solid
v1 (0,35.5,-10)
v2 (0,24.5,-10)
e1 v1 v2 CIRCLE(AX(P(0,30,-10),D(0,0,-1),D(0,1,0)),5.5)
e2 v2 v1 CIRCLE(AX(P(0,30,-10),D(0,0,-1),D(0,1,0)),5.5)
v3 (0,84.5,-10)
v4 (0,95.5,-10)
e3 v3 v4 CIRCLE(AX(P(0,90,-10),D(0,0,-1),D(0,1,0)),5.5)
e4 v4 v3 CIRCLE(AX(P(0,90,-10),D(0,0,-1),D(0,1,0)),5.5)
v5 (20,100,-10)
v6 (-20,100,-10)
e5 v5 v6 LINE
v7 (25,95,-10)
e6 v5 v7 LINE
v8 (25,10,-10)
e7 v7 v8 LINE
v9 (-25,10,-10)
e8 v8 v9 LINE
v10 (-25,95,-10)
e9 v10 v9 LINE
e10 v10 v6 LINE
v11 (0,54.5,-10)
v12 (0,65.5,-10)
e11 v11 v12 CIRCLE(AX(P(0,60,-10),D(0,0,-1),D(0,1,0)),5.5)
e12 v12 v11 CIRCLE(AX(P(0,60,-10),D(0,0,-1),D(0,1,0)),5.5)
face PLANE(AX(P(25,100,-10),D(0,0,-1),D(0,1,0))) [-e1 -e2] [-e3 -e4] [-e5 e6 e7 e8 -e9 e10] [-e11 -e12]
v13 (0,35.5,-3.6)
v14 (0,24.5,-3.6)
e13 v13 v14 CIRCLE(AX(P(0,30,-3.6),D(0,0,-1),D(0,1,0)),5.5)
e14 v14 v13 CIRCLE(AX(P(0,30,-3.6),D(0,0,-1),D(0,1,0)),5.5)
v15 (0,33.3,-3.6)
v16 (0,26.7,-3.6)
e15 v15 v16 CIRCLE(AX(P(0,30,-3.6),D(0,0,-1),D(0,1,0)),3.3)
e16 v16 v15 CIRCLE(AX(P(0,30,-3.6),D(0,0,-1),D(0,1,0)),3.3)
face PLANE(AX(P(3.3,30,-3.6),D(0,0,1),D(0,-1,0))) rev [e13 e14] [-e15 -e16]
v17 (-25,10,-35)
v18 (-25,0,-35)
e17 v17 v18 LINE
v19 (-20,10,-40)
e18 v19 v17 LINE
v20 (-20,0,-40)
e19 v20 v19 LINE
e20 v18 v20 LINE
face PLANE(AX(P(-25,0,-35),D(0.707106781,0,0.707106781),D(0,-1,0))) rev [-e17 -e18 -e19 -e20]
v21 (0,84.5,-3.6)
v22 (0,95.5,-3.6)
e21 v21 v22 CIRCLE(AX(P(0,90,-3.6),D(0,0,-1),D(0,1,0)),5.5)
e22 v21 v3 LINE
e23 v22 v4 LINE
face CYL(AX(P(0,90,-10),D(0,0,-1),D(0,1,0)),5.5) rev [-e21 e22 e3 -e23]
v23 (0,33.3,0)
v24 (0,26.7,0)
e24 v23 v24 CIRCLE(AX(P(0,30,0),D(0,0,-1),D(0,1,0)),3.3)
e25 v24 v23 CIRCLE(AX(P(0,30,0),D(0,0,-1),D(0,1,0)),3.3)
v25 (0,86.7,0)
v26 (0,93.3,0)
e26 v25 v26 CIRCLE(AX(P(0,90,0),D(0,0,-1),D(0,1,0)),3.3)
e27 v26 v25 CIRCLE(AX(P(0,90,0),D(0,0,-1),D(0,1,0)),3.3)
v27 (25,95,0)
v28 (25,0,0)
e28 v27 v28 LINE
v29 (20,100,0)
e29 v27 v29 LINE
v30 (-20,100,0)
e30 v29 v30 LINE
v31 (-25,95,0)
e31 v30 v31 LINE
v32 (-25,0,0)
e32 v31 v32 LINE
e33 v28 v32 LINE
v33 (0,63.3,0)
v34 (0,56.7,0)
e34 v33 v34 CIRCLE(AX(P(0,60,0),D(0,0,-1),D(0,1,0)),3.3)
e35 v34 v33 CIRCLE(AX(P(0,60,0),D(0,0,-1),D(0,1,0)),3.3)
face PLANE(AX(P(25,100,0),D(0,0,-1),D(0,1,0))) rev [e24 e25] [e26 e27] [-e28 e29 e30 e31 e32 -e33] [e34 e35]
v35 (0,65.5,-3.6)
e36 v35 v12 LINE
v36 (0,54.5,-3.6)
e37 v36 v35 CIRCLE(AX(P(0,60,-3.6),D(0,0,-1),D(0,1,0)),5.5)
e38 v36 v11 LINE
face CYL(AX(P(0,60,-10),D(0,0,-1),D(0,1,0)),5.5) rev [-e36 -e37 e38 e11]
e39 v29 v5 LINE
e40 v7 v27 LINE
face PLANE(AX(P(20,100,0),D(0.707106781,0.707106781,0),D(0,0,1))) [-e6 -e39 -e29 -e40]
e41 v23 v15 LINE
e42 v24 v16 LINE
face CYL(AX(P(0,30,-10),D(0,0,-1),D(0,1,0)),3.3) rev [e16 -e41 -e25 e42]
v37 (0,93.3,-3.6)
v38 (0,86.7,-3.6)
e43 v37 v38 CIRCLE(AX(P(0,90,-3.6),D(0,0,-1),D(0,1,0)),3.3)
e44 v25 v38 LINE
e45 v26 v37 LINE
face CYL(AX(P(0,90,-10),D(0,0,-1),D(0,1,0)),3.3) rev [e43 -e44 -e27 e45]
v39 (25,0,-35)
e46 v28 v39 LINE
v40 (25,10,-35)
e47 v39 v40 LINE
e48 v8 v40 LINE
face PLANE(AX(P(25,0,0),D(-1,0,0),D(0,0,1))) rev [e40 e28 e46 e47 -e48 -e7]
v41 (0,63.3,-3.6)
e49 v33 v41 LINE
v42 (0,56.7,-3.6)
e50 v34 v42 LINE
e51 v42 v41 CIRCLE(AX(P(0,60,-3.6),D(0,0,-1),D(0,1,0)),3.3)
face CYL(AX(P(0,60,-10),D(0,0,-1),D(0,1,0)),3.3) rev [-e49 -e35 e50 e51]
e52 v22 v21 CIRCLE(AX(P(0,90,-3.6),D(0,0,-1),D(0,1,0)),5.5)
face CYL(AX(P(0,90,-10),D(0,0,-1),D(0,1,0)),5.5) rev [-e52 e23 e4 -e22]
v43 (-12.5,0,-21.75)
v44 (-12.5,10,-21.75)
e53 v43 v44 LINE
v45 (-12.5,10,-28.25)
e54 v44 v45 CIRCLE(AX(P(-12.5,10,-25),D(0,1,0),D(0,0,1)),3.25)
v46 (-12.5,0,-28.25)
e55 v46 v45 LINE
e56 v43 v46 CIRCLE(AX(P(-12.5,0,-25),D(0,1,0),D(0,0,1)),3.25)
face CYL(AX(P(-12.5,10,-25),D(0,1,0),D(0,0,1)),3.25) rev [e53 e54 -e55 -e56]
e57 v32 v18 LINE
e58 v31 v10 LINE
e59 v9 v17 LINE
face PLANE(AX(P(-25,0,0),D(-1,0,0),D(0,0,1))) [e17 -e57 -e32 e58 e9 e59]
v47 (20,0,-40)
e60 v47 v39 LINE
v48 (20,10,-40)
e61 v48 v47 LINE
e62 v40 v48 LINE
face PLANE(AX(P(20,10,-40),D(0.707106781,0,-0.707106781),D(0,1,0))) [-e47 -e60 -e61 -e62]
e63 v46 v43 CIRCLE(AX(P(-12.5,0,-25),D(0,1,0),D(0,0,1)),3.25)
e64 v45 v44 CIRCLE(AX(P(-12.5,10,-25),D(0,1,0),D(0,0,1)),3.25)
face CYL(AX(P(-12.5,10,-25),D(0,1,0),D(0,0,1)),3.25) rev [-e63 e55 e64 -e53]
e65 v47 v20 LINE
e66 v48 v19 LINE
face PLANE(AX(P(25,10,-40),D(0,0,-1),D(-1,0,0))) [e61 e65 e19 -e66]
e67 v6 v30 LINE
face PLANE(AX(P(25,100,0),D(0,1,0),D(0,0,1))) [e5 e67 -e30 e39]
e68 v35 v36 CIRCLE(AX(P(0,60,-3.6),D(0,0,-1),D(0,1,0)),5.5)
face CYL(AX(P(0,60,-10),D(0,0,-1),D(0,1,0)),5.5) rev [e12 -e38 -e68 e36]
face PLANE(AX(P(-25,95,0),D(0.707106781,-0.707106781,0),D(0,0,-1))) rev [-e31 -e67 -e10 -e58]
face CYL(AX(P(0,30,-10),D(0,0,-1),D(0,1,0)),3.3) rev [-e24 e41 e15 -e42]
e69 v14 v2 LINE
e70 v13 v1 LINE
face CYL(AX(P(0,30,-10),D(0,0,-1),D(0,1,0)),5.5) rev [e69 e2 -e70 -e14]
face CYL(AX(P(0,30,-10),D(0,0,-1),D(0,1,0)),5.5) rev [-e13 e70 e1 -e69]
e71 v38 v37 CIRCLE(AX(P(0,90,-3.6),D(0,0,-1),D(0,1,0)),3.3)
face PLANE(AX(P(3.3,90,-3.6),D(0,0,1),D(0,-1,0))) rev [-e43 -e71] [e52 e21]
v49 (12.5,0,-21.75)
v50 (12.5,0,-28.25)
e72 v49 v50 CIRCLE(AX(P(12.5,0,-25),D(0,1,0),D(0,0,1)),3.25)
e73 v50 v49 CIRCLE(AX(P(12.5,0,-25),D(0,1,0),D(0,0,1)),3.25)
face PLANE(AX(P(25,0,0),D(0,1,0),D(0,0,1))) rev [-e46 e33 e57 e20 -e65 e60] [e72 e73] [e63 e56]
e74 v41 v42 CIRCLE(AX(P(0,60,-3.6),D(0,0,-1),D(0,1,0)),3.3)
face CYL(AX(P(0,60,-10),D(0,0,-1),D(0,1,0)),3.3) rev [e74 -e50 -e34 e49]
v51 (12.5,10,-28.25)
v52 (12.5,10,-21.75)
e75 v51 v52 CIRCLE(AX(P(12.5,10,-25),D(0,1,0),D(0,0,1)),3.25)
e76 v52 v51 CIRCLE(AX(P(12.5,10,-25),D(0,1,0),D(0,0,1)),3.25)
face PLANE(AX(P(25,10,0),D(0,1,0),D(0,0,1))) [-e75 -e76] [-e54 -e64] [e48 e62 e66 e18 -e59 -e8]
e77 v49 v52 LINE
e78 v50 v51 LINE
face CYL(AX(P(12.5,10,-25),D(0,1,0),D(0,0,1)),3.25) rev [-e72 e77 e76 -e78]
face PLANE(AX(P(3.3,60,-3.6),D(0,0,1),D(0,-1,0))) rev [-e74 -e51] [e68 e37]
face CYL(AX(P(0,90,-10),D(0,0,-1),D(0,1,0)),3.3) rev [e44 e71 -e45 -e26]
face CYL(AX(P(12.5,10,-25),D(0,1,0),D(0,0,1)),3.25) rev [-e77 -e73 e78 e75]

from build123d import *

# Parameters (mm, degrees)
EXTRUDE_2_DEPTH              = 25
HOLE_WIZARD_6_5_6_5_1_D      = 6.5
HOLE_WIZARD_M6_1_D           = 6.6
HOLE_WIZARD_M6_1_CBORE_D     = 11
HOLE_WIZARD_M6_1_CBORE_DEPTH = 6.4
CHAMFER_1_SIZE               = 5


with BuildPart() as part:
    # 草图2 → 拉伸-薄壁2 (new, symmetric)
    with BuildSketch(Plane(origin=(0, 0, 0), x_dir=(0, 0, -1), z_dir=(1, 0, 0))):
        Polygon((0, 100), (0, 0), (40, 0), (40, 10), (10, 10), (10, 100), align=None)
    extrude(amount=EXTRUDE_2_DEPTH, both=True)

    # Ø6.5 (6.5) 直径孔1 (through all)
    with Locations(Plane(origin=(0, 10, 0), x_dir=(1, 0, 0), z_dir=(0, 1, 0))):
        with Locations((-12.5, 25), (12.5, 25)):
            Hole(HOLE_WIZARD_6_5_6_5_1_D / 2)

    # M6 六角凹头螺钉的柱形沉头孔1 (through all)
    with Locations(Plane(origin=(0, 0, -10), x_dir=(-1, 0, 0), z_dir=(0, 0, -1))):
        with Locations((0, 90), (0, 60), (0, 30)):
            CounterBoreHole(HOLE_WIZARD_M6_1_D / 2, HOLE_WIZARD_M6_1_CBORE_D / 2, HOLE_WIZARD_M6_1_CBORE_DEPTH)

    # 倒角1
    chamfer_1_edges = [part.edges().sort_by_distance(p)[0] for p in [
        (25, 100, -5),
        (-25, 100, -5),
        (-25, 5, -40),
        (25, 5, -40),
    ]]
    chamfer(chamfer_1_edges, length=CHAMFER_1_SIZE)


solid = part.part
